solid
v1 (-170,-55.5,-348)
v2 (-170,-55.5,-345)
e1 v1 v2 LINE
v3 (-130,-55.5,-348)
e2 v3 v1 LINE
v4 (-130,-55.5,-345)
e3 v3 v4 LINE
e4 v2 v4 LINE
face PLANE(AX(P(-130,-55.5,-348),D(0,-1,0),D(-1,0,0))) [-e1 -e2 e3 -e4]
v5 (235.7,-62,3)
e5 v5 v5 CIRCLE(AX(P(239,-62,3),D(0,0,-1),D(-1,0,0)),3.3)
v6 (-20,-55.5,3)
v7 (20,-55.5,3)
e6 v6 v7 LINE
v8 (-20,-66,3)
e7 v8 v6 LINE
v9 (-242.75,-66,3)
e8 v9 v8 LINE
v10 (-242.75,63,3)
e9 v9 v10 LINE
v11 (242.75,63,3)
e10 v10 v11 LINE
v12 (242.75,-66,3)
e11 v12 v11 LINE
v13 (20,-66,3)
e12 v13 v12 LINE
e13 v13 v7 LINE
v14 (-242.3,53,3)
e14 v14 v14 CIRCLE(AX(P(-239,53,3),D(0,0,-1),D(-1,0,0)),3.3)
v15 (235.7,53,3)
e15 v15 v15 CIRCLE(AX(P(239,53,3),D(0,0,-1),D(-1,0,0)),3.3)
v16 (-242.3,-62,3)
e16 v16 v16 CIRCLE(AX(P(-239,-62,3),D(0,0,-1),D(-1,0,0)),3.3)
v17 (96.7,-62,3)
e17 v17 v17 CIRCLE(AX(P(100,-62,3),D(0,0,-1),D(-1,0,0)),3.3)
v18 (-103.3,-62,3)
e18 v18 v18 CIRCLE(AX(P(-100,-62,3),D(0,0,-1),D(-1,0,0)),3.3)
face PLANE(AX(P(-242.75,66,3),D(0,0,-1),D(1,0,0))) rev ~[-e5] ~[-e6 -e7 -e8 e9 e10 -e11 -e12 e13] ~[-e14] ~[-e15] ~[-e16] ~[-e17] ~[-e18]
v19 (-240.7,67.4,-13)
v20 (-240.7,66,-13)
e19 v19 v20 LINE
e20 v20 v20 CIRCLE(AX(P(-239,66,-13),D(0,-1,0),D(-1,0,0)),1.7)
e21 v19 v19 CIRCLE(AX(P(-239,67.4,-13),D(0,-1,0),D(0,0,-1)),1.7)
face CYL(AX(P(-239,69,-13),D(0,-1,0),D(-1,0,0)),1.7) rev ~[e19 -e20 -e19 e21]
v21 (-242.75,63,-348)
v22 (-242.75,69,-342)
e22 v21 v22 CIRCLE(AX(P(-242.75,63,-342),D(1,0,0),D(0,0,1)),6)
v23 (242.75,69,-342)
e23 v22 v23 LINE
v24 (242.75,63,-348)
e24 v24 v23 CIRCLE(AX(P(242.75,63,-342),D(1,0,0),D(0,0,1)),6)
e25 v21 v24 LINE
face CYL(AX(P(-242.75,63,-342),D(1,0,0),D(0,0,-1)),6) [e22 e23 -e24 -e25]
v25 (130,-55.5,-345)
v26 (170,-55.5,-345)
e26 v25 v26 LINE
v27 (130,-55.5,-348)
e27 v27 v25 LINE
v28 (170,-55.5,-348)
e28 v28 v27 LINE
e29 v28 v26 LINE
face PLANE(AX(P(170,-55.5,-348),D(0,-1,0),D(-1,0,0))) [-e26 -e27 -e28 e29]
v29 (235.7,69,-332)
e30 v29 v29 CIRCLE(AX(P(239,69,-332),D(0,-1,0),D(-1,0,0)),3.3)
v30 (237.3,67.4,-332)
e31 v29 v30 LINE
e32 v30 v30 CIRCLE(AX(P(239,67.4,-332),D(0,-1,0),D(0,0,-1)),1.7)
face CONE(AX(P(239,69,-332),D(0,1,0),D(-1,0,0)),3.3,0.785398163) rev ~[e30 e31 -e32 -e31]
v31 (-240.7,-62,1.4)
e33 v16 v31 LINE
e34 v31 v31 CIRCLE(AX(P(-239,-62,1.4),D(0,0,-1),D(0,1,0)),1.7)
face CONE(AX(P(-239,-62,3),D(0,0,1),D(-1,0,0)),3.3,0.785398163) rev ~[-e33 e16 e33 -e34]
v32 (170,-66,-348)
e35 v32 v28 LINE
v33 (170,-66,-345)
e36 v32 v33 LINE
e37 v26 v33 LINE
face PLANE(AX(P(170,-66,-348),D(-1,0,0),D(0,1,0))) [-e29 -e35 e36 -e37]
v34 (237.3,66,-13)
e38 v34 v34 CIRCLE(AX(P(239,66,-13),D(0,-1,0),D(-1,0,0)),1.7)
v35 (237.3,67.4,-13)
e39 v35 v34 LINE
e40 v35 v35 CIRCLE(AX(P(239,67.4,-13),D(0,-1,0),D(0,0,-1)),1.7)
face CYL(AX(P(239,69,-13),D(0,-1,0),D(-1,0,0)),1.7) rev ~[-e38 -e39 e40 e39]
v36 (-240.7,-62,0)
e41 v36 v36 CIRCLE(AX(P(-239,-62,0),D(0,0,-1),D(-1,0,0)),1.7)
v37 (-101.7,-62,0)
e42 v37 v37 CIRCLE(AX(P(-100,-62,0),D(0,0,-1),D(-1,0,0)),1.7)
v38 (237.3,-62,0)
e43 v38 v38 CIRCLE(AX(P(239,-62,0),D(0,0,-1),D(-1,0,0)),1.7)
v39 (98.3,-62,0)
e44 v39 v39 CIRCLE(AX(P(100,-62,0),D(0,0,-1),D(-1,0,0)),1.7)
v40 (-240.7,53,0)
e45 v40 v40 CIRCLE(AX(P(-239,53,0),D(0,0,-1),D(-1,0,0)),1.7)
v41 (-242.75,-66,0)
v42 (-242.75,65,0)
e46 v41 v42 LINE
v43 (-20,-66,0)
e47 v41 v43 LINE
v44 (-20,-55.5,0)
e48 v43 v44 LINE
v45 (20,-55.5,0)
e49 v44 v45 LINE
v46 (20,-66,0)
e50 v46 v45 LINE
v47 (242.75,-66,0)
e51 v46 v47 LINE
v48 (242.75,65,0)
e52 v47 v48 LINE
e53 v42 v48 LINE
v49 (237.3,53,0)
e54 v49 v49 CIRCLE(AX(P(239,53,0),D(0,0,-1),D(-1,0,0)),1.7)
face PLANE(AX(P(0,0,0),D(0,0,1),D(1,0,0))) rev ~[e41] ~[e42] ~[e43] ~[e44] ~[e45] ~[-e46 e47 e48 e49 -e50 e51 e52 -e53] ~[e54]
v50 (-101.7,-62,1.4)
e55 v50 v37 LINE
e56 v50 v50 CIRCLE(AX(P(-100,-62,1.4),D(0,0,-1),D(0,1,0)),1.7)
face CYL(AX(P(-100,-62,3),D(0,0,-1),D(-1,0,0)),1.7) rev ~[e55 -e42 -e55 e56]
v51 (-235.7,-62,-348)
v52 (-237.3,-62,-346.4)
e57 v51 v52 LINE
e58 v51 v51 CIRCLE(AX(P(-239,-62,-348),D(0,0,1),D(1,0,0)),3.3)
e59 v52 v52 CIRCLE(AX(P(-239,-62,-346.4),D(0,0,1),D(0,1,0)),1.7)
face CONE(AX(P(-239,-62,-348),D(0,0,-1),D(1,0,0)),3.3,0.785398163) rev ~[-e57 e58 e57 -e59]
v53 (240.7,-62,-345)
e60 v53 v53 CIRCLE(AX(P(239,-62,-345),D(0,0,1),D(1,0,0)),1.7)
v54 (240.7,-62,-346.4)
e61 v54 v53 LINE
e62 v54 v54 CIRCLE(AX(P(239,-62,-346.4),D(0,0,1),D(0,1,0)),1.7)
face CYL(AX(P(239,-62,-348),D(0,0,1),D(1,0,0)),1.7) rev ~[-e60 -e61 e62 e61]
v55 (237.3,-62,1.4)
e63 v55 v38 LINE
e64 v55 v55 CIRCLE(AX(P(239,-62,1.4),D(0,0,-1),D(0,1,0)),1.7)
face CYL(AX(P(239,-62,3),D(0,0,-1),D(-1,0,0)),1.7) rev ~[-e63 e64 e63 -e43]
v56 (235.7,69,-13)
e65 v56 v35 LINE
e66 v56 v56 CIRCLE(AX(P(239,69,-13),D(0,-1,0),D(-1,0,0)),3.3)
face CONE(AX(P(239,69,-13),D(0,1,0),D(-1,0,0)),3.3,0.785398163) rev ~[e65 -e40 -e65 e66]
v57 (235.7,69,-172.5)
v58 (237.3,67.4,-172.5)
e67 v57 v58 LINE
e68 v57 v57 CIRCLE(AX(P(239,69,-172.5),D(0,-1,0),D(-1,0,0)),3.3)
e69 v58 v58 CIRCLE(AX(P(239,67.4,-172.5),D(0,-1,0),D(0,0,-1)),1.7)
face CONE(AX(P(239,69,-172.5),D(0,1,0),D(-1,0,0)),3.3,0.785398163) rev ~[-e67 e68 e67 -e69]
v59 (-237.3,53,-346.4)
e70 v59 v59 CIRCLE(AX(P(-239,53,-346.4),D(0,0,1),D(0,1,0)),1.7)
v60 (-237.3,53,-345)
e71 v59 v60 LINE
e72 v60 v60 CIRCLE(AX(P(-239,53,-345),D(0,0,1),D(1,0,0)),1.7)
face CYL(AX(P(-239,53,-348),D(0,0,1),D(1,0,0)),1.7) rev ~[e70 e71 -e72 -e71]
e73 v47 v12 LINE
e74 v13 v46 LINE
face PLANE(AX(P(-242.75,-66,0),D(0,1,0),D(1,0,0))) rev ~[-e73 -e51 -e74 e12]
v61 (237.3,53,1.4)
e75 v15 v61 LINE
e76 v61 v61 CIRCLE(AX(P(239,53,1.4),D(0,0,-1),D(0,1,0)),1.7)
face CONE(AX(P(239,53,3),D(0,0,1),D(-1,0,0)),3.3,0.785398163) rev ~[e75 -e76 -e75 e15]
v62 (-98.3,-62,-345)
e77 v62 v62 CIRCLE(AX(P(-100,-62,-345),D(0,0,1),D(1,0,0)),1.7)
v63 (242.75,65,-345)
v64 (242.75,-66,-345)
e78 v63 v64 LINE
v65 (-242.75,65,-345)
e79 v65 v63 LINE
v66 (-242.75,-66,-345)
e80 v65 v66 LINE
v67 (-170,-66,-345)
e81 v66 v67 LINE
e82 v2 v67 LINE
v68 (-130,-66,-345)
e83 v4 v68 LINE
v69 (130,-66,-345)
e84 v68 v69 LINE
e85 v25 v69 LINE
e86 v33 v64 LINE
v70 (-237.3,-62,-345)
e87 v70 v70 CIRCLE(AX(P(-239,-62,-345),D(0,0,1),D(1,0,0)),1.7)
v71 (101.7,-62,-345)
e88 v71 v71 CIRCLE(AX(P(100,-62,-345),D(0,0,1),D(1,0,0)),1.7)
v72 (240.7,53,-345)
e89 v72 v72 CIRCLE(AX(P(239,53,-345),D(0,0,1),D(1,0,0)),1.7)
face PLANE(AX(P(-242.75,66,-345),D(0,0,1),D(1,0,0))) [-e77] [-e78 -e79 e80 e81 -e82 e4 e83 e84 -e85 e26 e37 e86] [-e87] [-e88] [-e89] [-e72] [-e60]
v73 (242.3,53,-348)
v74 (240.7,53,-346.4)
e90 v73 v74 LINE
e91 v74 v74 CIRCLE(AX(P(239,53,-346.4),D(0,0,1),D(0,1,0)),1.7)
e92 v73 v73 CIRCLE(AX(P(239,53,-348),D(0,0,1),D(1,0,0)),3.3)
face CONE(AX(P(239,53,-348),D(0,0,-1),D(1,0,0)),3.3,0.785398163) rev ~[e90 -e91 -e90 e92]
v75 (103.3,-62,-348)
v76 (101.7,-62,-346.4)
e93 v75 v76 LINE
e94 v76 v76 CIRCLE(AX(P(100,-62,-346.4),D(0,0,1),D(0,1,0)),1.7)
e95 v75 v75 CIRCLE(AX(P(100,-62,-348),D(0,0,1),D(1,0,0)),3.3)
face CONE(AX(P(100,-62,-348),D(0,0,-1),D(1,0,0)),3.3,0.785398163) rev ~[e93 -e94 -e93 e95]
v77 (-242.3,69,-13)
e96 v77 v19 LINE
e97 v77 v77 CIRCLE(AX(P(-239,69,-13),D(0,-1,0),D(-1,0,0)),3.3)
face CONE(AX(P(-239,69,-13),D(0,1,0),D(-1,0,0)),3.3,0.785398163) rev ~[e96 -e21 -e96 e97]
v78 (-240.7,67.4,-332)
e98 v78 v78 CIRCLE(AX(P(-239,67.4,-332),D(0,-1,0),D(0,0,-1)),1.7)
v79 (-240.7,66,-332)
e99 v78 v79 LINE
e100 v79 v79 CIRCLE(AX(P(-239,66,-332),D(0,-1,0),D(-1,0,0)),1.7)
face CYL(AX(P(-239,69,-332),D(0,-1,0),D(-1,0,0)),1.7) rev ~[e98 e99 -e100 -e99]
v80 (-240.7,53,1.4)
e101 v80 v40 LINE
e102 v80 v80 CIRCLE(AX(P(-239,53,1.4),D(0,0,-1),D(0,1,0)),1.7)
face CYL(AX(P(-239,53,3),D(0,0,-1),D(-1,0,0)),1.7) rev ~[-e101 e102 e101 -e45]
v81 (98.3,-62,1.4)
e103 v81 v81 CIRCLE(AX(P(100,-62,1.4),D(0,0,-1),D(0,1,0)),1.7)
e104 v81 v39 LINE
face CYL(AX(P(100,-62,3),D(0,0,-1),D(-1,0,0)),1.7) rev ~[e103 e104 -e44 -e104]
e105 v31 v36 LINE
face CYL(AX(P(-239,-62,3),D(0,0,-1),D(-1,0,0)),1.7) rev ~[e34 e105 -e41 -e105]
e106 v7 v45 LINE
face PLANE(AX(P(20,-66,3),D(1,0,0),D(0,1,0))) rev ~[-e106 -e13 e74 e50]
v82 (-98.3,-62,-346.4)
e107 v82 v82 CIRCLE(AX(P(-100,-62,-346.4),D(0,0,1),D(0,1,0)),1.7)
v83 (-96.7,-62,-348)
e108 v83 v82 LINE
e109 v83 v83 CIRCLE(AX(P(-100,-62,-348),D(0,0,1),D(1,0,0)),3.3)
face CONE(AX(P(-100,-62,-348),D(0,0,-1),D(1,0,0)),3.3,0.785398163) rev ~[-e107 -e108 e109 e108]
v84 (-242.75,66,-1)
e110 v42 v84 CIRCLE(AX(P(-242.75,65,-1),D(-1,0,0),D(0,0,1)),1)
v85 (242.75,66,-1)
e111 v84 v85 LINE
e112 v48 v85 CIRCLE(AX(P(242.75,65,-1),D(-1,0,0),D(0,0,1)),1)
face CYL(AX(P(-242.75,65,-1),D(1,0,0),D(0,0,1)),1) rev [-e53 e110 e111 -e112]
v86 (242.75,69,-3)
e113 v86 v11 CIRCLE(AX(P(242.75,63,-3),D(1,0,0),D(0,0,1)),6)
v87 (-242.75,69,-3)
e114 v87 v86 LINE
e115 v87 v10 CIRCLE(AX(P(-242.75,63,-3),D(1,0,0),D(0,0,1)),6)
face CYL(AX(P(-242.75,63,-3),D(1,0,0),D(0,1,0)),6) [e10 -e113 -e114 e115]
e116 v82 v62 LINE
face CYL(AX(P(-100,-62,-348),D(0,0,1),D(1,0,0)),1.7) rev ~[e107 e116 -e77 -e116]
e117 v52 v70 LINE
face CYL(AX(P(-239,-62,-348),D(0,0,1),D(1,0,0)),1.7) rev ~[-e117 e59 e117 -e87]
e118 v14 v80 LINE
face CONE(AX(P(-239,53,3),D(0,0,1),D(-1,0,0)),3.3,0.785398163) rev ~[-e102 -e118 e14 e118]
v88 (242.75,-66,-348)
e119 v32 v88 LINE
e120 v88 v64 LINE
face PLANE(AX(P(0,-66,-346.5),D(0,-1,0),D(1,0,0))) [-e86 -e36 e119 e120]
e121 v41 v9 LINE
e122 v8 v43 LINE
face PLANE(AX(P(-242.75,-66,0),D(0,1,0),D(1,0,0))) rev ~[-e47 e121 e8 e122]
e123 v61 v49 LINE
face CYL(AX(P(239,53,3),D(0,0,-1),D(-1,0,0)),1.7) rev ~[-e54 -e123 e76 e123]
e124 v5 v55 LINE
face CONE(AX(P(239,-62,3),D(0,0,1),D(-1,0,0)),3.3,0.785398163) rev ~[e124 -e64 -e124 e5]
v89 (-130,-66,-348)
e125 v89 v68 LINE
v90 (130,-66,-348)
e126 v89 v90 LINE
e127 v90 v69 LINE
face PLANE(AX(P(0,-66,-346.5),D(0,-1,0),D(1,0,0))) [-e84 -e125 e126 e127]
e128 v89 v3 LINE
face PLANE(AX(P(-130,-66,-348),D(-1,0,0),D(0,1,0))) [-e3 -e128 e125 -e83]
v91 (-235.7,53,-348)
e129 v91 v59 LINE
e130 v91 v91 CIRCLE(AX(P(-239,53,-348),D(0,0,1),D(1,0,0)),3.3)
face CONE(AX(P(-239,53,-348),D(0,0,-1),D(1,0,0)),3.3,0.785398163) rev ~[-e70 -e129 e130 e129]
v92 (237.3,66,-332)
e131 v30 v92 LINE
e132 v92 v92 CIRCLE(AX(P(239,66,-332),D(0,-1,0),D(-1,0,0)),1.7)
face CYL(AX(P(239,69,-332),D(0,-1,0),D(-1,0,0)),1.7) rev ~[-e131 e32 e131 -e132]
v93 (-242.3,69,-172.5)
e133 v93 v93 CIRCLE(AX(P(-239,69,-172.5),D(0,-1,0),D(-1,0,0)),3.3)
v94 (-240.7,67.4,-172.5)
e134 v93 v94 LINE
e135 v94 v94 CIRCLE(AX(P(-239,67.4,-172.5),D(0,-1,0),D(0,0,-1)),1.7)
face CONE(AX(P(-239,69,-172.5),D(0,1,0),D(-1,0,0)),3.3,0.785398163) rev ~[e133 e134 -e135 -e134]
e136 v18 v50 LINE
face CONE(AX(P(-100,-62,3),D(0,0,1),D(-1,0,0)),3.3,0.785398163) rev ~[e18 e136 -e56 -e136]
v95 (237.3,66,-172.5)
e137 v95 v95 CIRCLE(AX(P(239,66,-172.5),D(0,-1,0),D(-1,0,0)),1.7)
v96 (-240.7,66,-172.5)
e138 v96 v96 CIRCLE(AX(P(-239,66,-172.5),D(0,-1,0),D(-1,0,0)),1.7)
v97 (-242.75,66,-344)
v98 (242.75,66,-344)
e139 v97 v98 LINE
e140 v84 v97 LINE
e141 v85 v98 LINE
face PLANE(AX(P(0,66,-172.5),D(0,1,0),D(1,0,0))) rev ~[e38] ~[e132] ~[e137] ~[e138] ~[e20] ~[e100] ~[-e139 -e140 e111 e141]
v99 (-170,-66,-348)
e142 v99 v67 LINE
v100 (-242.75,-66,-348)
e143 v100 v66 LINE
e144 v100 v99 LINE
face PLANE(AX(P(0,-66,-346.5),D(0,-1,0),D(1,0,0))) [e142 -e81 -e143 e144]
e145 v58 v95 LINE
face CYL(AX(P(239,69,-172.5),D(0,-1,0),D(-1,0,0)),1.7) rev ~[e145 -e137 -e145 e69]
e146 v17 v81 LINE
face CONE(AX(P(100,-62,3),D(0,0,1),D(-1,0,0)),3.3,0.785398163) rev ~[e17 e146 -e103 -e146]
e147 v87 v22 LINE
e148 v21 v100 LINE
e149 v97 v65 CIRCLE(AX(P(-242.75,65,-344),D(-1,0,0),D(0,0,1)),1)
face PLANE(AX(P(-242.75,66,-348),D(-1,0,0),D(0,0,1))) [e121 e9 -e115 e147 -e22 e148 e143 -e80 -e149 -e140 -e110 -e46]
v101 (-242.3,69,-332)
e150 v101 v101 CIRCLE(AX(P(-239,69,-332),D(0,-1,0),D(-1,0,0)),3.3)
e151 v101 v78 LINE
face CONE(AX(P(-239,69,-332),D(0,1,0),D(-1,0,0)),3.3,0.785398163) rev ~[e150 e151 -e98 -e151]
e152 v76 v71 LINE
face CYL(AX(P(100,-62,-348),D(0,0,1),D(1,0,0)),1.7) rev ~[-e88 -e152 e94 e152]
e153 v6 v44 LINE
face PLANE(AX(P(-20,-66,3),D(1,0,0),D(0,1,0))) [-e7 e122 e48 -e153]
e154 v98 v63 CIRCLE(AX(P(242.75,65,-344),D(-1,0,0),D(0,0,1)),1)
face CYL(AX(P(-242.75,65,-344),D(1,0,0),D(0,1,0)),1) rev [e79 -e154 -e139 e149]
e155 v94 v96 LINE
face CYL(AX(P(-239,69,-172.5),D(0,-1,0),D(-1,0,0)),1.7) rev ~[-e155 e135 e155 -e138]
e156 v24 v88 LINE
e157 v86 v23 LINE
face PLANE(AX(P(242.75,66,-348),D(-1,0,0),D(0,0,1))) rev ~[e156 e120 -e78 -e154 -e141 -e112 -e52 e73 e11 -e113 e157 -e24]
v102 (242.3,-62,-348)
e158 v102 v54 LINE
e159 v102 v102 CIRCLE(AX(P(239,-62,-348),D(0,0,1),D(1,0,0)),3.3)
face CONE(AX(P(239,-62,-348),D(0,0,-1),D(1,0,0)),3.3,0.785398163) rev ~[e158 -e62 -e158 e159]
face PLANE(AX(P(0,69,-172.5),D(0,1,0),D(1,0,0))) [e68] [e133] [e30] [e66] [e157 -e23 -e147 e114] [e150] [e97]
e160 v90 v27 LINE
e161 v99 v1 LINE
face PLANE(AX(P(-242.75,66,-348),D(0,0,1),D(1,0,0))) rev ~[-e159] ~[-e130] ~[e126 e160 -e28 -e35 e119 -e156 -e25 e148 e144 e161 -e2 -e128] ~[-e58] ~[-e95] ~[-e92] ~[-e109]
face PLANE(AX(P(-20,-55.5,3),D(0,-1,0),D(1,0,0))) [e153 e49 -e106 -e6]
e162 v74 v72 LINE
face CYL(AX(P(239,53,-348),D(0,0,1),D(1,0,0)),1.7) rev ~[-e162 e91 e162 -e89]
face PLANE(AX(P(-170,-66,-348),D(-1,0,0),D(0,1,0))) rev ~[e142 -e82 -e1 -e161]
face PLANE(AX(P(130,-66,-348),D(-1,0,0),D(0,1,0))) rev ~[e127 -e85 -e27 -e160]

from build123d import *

# Parameters (mm, degrees)
SKETCH1_W                                       = 485.5
SKETCH1_H                                       = 132
BOSS_EXTRUDE1_DEPTH                             = 3
SKETCH2_W                                       = 485.5
SKETCH2_H                                       = 351
BOSS_EXTRUDE2_DEPTH                             = 3
SKETCH3_W                                       = 485.5
SKETCH3_H                                       = 3
BOSS_EXTRUDE3_DEPTH                             = 132
FILLET1_R                                       = 1
FILLET2_R                                       = 6
SKETCH4_W                                       = 40
SKETCH4_H                                       = 10.5
CUT_EXTRUDE1_DEPTH                              = 4.5
SKETCH5_W                                       = 40
SKETCH5_H                                       = 10.5
CUT_EXTRUDE2_DEPTH                              = 4.5
CROSS_RECESS_WOOD_SCREW_HOLE_TYPE_1_D           = 3.4
CROSS_RECESS_WOOD_SCREW_HOLE_TYPE_1_CSINK_D     = 6.6
CROSS_RECESS_WOOD_SCREW_HOLE_TYPE_1_CSINK_ANGLE = 90
CROSS_RECESS_WOOD_SCREW_HOLE_TYPE_2_D           = 3.4
CROSS_RECESS_WOOD_SCREW_HOLE_TYPE_2_DEPTH       = 6.5
CROSS_RECESS_WOOD_SCREW_HOLE_TYPE_2_CSINK_D     = 6.6
CROSS_RECESS_WOOD_SCREW_HOLE_TYPE_2_CSINK_ANGLE = 90
CROSS_RECESS_WOOD_SCREW_HOLE_TYPE_2_TIP         = 1.021463052
CROSS_RECESS_WOOD_SCREW_HOLE_TYPE_3_D           = 3.4
CROSS_RECESS_WOOD_SCREW_HOLE_TYPE_3_DEPTH       = 6.5
CROSS_RECESS_WOOD_SCREW_HOLE_TYPE_3_CSINK_D     = 6.6
CROSS_RECESS_WOOD_SCREW_HOLE_TYPE_3_CSINK_ANGLE = 90
CROSS_RECESS_WOOD_SCREW_HOLE_TYPE_3_TIP         = 1.021463052


with BuildPart() as part:
    # Sketch1 → Boss-Extrude1 (new body)
    with BuildSketch(Plane.XY):
        Rectangle(SKETCH1_W, SKETCH1_H)
    extrude(amount=BOSS_EXTRUDE1_DEPTH)

    # Sketch2 → Boss-Extrude2 (add)
    with BuildSketch(Plane(origin=(0, 66, 0), x_dir=(1, 0, 0), z_dir=(0, 1, 0))):
        with Locations((0, 172.5)):
            Rectangle(SKETCH2_W, SKETCH2_H)
    extrude(amount=BOSS_EXTRUDE2_DEPTH)

    # Sketch3 → Boss-Extrude3 (add)
    with BuildSketch(Plane.XZ.offset(-66)):
        with Locations((0, -346.5)):
            Rectangle(SKETCH3_W, SKETCH3_H)
    extrude(amount=BOSS_EXTRUDE3_DEPTH)

    # Fillet1
    fillet1_edges = [part.edges().sort_by_distance(p)[0] for p in [
        (0, 66, -345),
        (0, 66, 0),
    ]]
    fillet(fillet1_edges, radius=FILLET1_R)

    # Fillet2
    fillet2_edges = [part.edges().sort_by_distance(p)[0] for p in [
        (0, 69, 3),
        (0, 69, -348),
    ]]
    fillet(fillet2_edges, radius=FILLET2_R)

    # Sketch4 → Cut-Extrude1 (cut)
    with BuildSketch(Plane.XY.offset(3)):
        with Locations((0, -60.75)):
            Rectangle(SKETCH4_W, SKETCH4_H)
    extrude(amount=-CUT_EXTRUDE1_DEPTH, mode=Mode.SUBTRACT)

    # Sketch5 → Cut-Extrude2 (cut)
    with BuildSketch(Plane(origin=(0, 0, -348), x_dir=(-1, 0, 0), z_dir=(0, 0, -1))):
        with Locations((150, -60.75)):
            Rectangle(SKETCH5_W, SKETCH5_H)
        with Locations((-150, -60.75)):
            Rectangle(SKETCH5_W, SKETCH5_H)
    extrude(amount=-CUT_EXTRUDE2_DEPTH, mode=Mode.SUBTRACT)

    # Cross recess wood screw hole type 1 (through all)
    with Locations(Plane(origin=(0, 69, 0), x_dir=(1, 0, 0), z_dir=(0, 1, 0))):
        with Locations((239, 332), (239, 172.5), (239, 13), (-239, 332), (-239, 172.5), (-239, 13)):
            CounterSinkHole(CROSS_RECESS_WOOD_SCREW_HOLE_TYPE_1_D / 2, CROSS_RECESS_WOOD_SCREW_HOLE_TYPE_1_CSINK_D / 2, counter_sink_angle=CROSS_RECESS_WOOD_SCREW_HOLE_TYPE_1_CSINK_ANGLE)

    # Cross recess wood screw hole type 2
    with Locations(Plane.XY.offset(3)):
        with Locations((-239, 53), (-239, -62), (-100, -62), (100, -62), (239, 53), (239, -62)):
            CounterSinkHole(CROSS_RECESS_WOOD_SCREW_HOLE_TYPE_2_D / 2, CROSS_RECESS_WOOD_SCREW_HOLE_TYPE_2_CSINK_D / 2, depth=CROSS_RECESS_WOOD_SCREW_HOLE_TYPE_2_DEPTH, counter_sink_angle=CROSS_RECESS_WOOD_SCREW_HOLE_TYPE_2_CSINK_ANGLE)
            with Locations((0, 0, -(CROSS_RECESS_WOOD_SCREW_HOLE_TYPE_2_DEPTH + CROSS_RECESS_WOOD_SCREW_HOLE_TYPE_2_TIP / 2))):  # 118° drill point
                Cone(0, CROSS_RECESS_WOOD_SCREW_HOLE_TYPE_2_D / 2, CROSS_RECESS_WOOD_SCREW_HOLE_TYPE_2_TIP, mode=Mode.SUBTRACT)

    # Cross recess wood screw hole type 3
    with Locations(Plane(origin=(0, 0, -348), x_dir=(-1, 0, 0), z_dir=(0, 0, -1))):
        with Locations((239, 53), (239, -62), (100, -62), (-100, -62), (-239, -62), (-239, 53)):
            CounterSinkHole(CROSS_RECESS_WOOD_SCREW_HOLE_TYPE_3_D / 2, CROSS_RECESS_WOOD_SCREW_HOLE_TYPE_3_CSINK_D / 2, depth=CROSS_RECESS_WOOD_SCREW_HOLE_TYPE_3_DEPTH, counter_sink_angle=CROSS_RECESS_WOOD_SCREW_HOLE_TYPE_3_CSINK_ANGLE)
            with Locations((0, 0, -(CROSS_RECESS_WOOD_SCREW_HOLE_TYPE_3_DEPTH + CROSS_RECESS_WOOD_SCREW_HOLE_TYPE_3_TIP / 2))):  # 118° drill point
                Cone(0, CROSS_RECESS_WOOD_SCREW_HOLE_TYPE_3_D / 2, CROSS_RECESS_WOOD_SCREW_HOLE_TYPE_3_TIP, mode=Mode.SUBTRACT)


solid = part.part
